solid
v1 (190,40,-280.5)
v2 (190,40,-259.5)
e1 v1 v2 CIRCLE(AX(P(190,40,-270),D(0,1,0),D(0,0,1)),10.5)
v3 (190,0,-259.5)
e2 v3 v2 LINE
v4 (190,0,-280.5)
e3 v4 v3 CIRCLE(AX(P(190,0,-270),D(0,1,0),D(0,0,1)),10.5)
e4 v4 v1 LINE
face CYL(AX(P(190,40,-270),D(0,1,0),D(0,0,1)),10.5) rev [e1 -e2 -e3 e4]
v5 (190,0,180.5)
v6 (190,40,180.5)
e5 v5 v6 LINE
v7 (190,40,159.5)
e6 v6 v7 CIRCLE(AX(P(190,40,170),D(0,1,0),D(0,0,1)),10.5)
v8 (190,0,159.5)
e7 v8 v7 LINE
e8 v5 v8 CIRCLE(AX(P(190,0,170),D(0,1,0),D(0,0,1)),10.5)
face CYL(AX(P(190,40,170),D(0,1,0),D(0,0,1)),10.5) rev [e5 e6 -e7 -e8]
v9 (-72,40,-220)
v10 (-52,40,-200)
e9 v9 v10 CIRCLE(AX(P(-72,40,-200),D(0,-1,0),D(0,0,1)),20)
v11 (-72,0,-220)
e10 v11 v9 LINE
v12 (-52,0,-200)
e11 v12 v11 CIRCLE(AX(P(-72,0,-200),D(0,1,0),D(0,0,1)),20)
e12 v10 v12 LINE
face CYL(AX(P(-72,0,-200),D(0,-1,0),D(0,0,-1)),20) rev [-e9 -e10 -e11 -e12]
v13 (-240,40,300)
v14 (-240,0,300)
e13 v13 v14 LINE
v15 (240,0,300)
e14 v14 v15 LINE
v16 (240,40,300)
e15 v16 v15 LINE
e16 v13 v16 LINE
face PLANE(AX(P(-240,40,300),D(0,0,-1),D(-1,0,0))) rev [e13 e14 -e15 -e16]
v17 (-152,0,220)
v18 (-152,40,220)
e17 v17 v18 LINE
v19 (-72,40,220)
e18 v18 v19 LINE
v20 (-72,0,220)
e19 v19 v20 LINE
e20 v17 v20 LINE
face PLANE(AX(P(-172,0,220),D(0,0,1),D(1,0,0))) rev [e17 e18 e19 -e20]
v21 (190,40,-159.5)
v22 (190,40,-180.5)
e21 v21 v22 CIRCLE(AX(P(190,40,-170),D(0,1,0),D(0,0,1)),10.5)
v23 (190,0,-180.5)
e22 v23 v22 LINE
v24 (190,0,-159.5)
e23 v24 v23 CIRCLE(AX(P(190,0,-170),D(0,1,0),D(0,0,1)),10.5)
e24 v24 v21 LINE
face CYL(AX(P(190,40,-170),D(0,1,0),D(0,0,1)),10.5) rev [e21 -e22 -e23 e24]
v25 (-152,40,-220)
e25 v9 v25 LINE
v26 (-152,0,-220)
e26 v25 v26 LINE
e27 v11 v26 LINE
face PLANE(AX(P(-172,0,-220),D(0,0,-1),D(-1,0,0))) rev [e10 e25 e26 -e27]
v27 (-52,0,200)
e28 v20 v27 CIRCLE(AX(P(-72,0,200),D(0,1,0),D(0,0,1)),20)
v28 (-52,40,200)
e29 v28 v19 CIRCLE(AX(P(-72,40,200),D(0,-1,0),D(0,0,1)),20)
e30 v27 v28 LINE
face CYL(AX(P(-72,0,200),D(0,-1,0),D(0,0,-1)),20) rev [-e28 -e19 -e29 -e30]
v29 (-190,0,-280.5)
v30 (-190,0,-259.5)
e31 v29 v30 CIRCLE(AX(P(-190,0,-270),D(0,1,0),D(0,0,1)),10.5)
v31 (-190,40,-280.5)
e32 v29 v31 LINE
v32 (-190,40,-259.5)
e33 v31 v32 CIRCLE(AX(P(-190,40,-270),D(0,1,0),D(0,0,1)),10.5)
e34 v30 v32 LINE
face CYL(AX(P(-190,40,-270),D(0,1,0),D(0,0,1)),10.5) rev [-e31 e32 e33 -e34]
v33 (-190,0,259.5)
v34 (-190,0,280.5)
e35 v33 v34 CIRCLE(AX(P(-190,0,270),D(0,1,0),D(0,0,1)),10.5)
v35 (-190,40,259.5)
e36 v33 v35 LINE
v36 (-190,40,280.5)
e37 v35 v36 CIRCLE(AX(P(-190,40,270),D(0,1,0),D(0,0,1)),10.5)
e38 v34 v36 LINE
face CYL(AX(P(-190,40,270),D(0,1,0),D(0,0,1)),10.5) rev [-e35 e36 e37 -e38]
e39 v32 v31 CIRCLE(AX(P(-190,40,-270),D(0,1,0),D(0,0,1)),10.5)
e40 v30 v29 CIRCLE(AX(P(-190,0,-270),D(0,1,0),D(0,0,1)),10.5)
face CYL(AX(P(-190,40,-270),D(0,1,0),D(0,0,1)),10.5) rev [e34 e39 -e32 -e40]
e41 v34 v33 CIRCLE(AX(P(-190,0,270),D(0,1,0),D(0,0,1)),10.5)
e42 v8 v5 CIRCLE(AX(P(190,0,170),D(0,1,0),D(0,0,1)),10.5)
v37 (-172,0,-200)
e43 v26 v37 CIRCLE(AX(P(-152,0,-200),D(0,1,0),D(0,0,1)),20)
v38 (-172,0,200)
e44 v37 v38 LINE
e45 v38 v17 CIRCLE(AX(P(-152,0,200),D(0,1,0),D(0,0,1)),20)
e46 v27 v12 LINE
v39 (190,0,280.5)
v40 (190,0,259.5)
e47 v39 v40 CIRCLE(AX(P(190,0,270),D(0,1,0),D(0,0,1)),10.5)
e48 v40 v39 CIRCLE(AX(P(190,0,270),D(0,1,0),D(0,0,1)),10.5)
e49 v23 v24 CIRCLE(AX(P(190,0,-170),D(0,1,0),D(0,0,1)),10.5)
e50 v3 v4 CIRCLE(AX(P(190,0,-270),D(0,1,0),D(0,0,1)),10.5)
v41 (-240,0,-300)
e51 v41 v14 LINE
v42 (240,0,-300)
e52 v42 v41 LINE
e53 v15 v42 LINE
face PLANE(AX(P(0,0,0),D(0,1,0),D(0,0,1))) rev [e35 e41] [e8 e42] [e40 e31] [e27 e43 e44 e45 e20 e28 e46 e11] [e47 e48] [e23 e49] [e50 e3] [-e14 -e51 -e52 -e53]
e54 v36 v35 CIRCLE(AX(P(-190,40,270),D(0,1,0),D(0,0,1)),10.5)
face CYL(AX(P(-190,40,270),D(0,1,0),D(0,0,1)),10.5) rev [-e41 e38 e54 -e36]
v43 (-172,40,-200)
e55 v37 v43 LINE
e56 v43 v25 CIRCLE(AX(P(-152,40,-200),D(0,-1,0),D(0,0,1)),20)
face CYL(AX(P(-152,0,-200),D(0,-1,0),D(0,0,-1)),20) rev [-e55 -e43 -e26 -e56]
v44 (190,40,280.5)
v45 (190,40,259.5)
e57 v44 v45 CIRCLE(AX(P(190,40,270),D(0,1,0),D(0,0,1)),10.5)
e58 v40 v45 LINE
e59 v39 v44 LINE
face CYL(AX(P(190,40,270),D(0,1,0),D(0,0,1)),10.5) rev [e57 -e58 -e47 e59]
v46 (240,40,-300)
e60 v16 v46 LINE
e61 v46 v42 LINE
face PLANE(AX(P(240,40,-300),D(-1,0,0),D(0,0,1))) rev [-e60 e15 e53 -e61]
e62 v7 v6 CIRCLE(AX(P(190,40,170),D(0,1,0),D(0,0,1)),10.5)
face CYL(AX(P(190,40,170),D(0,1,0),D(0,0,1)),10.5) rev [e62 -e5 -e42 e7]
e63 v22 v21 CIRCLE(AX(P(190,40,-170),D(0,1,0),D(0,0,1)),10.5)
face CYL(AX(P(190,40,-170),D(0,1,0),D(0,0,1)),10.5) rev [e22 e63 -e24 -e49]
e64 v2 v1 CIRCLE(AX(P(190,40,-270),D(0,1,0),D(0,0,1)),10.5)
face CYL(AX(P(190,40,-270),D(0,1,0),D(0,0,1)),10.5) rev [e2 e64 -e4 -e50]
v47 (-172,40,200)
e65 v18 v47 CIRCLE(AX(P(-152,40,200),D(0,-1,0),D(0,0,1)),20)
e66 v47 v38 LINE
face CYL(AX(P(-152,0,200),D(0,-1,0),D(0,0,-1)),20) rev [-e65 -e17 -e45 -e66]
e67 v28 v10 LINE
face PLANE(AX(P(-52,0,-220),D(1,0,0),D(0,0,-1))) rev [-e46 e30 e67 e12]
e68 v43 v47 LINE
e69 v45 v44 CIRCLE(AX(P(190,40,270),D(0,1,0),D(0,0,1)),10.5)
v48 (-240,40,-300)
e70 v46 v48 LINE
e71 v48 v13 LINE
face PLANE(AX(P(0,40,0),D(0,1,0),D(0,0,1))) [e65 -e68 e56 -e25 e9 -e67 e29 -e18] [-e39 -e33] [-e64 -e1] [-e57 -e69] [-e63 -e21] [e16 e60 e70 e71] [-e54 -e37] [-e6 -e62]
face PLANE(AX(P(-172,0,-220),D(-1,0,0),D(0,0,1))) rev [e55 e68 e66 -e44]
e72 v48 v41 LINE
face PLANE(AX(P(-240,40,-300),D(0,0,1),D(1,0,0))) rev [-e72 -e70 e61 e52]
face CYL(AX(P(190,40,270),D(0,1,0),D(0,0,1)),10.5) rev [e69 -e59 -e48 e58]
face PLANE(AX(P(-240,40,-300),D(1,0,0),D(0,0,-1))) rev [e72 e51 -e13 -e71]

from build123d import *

# Parameters (mm, degrees)
SKETCH1_W           = 480
SKETCH1_H           = 600
BOSS_EXTRUDE1_DEPTH = 40
SKETCH4_W           = 120
SKETCH4_H           = 440
CUT_EXTRUDE3_DEPTH  = 387.264158317
FILLET1_R           = 20
M24_TAPPED_HOLE1_D  = 21


with BuildPart() as part:
    # Sketch1 → Boss-Extrude1 (new body)
    with BuildSketch(Plane(origin=(0, 0, 0), x_dir=(1, 0, 0), z_dir=(0, 1, 0))):
        Rectangle(SKETCH1_W, SKETCH1_H)
    extrude(amount=BOSS_EXTRUDE1_DEPTH)

    # Sketch4 → Cut-Extrude3 (cut, through all)
    with BuildSketch(Plane(origin=(0, 40, 0), x_dir=(1, 0, 0), z_dir=(0, 1, 0))):
        with Locations((-112, 0)):
            Rectangle(SKETCH4_W, SKETCH4_H)
    extrude(amount=-CUT_EXTRUDE3_DEPTH, mode=Mode.SUBTRACT)

    # Fillet1
    fillet1_edges = [part.edges().sort_by_distance(p)[0] for p in [
        (-52, 20, -220),
        (-52, 20, 220),
        (-172, 20, 220),
        (-172, 20, -220),
    ]]
    fillet(fillet1_edges, radius=FILLET1_R)

    # M24 Tapped Hole1 (through all)
    with Locations(Plane(origin=(0, 40, 0), x_dir=(1, 0, 0), z_dir=(0, 1, 0))):
        with Locations((-190, -270), (-190, 270), (190, 270), (190, -270), (190, 170), (190, -170)):
            Hole(M24_TAPPED_HOLE1_D / 2)


solid = part.part
